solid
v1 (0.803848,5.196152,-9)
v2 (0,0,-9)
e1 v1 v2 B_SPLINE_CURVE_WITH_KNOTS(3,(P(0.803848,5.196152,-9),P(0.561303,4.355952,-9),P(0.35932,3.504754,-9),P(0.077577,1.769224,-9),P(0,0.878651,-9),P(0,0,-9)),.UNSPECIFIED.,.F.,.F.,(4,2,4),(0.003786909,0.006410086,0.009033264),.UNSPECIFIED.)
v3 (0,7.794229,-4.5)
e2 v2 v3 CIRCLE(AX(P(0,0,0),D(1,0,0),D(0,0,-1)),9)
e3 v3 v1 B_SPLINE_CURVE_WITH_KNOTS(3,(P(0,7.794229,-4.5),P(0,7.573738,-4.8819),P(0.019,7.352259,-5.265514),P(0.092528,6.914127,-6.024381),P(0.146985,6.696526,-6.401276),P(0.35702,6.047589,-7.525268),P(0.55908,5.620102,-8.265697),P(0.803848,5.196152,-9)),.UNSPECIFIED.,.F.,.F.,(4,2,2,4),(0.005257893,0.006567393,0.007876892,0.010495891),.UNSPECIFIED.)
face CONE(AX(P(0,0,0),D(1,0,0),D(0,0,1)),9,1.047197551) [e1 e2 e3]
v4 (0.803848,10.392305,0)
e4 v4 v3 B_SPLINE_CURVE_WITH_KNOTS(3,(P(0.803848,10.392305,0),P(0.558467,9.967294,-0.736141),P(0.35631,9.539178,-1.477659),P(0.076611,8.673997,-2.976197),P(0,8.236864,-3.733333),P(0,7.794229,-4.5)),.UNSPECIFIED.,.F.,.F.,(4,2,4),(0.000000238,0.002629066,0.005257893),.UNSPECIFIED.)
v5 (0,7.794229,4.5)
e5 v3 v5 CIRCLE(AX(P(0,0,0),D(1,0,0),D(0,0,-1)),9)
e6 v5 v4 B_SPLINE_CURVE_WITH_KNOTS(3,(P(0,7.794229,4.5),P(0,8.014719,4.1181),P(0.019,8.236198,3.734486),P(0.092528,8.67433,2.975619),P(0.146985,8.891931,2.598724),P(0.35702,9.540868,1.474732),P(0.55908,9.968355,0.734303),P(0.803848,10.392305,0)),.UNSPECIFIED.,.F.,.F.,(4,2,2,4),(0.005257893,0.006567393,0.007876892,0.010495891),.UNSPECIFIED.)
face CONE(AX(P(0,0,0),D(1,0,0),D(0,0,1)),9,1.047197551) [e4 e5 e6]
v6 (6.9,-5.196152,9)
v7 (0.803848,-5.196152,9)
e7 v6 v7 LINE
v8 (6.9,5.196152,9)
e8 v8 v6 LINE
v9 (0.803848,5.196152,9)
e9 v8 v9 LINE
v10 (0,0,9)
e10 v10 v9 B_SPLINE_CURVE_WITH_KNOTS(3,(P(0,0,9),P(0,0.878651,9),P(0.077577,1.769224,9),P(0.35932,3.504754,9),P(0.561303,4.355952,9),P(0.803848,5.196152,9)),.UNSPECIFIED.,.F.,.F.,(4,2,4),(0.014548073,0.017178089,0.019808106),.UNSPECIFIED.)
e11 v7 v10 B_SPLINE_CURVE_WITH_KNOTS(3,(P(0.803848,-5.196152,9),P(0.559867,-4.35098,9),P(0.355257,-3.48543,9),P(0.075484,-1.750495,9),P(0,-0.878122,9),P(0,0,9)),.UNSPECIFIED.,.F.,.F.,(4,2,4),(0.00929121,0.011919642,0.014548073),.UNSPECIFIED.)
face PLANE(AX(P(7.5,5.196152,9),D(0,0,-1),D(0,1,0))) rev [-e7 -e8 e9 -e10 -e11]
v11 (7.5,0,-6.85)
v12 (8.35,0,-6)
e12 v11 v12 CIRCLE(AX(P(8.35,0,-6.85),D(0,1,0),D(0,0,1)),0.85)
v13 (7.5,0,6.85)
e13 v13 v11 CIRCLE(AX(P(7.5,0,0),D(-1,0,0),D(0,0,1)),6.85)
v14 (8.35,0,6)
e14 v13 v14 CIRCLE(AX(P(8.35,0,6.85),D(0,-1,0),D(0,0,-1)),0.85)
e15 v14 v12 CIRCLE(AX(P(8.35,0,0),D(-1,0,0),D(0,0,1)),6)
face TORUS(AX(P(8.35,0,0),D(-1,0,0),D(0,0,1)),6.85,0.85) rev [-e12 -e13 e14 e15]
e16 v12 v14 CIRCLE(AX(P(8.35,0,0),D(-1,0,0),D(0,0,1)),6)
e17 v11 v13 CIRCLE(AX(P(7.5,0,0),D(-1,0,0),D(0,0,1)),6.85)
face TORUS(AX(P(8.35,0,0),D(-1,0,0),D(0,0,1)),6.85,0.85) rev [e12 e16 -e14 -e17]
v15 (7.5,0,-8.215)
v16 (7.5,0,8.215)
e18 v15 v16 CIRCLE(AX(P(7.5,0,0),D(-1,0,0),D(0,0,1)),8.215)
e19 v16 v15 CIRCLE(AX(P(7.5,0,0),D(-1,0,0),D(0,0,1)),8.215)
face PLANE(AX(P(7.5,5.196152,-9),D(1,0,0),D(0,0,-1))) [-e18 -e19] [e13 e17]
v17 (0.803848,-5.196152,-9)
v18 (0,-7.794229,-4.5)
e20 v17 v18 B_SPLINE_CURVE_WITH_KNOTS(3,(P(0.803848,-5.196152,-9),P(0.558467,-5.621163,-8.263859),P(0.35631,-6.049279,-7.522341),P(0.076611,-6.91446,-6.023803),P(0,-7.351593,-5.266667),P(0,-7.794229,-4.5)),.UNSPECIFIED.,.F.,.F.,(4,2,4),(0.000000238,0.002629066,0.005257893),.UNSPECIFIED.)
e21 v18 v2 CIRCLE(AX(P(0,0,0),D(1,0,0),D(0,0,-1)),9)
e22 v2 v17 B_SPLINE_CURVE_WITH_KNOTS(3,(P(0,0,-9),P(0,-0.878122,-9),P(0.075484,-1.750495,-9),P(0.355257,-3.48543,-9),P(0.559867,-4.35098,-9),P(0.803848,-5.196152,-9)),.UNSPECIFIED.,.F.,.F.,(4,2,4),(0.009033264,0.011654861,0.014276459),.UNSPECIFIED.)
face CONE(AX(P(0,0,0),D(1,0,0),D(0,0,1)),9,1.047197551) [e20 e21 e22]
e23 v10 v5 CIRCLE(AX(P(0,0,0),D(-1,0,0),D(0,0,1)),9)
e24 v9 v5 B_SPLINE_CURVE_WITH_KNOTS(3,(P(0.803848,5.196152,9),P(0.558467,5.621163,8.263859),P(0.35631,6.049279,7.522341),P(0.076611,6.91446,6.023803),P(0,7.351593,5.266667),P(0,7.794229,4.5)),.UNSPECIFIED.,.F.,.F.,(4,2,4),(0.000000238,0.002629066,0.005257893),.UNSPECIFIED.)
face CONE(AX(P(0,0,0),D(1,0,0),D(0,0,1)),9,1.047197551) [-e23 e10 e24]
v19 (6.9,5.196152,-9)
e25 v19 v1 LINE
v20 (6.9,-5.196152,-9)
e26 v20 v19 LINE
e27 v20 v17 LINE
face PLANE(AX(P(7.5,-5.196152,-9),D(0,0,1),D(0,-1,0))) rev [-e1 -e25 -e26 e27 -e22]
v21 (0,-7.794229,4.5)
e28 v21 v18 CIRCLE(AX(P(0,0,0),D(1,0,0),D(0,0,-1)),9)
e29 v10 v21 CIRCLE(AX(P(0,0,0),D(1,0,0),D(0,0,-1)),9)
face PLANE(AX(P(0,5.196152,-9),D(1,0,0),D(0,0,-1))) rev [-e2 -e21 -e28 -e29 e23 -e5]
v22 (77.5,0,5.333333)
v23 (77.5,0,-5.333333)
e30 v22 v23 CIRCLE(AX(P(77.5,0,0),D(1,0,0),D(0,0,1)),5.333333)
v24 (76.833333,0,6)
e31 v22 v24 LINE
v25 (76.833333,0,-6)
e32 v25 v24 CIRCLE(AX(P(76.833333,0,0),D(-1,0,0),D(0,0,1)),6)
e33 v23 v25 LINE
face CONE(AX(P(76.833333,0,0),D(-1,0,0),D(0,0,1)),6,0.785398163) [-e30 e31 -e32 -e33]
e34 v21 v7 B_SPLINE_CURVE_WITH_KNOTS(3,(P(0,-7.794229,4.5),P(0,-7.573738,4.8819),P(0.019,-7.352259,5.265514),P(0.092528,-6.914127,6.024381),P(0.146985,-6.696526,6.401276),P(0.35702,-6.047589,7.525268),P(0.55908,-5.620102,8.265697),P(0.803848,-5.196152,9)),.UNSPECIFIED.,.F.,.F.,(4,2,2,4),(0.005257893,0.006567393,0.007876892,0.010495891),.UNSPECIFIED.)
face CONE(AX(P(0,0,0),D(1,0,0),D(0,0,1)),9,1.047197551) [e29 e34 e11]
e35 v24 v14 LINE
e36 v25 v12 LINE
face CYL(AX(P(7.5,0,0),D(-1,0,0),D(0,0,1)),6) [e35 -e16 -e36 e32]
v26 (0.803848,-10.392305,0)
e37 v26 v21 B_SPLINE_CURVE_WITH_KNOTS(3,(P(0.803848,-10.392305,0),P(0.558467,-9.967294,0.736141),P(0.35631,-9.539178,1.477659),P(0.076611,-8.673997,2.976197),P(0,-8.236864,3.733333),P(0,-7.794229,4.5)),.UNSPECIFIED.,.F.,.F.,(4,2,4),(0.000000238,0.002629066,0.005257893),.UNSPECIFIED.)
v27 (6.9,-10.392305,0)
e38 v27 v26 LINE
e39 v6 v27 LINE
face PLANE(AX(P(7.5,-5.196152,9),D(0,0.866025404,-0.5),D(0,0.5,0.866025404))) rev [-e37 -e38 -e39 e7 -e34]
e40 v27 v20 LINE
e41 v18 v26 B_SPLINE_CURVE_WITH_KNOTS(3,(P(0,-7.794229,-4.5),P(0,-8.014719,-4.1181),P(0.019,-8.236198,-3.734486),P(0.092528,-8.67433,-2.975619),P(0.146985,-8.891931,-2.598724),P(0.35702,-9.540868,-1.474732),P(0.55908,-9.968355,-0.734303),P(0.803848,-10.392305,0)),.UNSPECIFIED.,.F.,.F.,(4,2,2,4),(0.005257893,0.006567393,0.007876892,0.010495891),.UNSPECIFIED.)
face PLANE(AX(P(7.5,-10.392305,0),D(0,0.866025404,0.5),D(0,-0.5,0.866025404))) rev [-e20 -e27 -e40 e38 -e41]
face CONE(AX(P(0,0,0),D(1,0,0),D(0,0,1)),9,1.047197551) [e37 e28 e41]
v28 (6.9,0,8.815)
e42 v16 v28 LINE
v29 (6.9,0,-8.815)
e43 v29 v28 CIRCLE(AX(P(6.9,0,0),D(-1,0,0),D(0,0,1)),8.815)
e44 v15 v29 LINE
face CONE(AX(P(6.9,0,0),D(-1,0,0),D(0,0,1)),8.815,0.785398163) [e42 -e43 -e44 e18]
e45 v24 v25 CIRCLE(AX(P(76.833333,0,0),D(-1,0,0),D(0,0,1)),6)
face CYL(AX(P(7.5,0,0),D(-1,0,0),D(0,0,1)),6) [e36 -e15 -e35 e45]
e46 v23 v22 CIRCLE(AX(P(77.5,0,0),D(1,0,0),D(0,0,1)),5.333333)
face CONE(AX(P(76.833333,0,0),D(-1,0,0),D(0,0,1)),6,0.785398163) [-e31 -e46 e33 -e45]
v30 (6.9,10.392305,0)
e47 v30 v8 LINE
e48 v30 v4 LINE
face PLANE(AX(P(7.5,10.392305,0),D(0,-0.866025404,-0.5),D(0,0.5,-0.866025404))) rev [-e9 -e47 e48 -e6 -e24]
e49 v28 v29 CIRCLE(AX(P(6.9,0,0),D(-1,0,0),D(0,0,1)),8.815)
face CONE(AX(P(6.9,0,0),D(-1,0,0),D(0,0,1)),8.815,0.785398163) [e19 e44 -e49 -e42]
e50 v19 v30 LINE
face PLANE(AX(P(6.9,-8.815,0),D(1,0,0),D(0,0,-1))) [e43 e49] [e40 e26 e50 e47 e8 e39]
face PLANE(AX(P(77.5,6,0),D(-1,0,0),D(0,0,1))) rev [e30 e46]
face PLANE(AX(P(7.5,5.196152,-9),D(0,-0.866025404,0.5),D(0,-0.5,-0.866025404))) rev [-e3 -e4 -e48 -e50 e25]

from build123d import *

# Parameters (mm, degrees)
BOSS_EXTRUDE1_DEPTH = 7.5
SKETCH4_R           = 20.03
SKETCH4_R_2         = 9
CUT_EXTRUDE1_DEPTH  = 0.9375
CUT_EXTRUDE1_DRAFT  = -60
CHAMFER2_SIZE       = 0.666666667


with BuildPart() as part:
    # Sketch3 → Boss-Extrude1 (new body)
    with BuildSketch(Plane(origin=(0, 0, 0), x_dir=(0, 0, -1), z_dir=(1, 0, 0))):
        Polygon((9, 5.196152423), (0, 10.392304845), (-9, 5.196152423), (-9, -5.196152423), (0, -10.392304845), (9, -5.196152423), align=None)
    extrude(amount=BOSS_EXTRUDE1_DEPTH)


with BuildPart() as cut_extrude1_tool:
    # Sketch4 → Cut-Extrude1 (with draft: the straight prism first)
    with BuildSketch(Plane.ZY):
        Circle(SKETCH4_R)
        Circle(SKETCH4_R_2, mode=Mode.SUBTRACT)
    extrude(amount=-CUT_EXTRUDE1_DEPTH)
    # Cut-Extrude1: the draft: its side faces are tilted about the plane it starts from
    cut_extrude1_sides = [cut_extrude1_tool.faces().sort_by_distance(p)[0] for p in [
        (0.46875, 0, -20.03),
        (0.46875, 0, -9),
    ]]
    draft(cut_extrude1_sides, Plane.ZY, CUT_EXTRUDE1_DRAFT)


with BuildPart() as part_1:
    add(part.part)

    # Cut-Extrude1: cut by cut_extrude1_tool
    add(cut_extrude1_tool.part, mode=Mode.SUBTRACT)

    # Sketch5 → Revolve1 (revolve)
    with BuildSketch(Plane.XY, mode=Mode.PRIVATE) as revolve1_sk:
        with BuildLine():
            Line((8.35, 6), (77.5, 6))
            Line((77.5, 6), (77.5, 0))
            Line((77.5, 0), (7.5, 0))
            Line((7.5, 0), (7.5, 6.85))
            ThreePointArc((7.5, 6.85), (7.748959236, 6.248959236), (8.35, 6))
        make_face()
    revolve(revolve1_sk.sketch.rotate(Axis((7.5, 0, 0), (1, 0, 0)), 90), axis=Axis((7.5, 0, 0), (1, 0, 0)))

    # Chamfer2
    chamfer2_edges = [part_1.edges().sort_by_distance(p)[0] for p in [
        (77.5, 0, -6),
    ]]
    chamfer(chamfer2_edges, length=CHAMFER2_SIZE)

    # Sketch7 → Cut-Revolve1 (revolve, cut)
    with BuildSketch(Plane.XY, mode=Mode.PRIVATE) as cut_revolve1_sk:
        Polygon((7.5, 8.215), (6.9, 8.815), (6.9, 20.03), (7.5, 20.03), align=None)
    revolve(cut_revolve1_sk.sketch.rotate(Axis((0, 0, 0), (1, 0, 0)), 90), axis=Axis((0, 0, 0), (1, 0, 0)), mode=Mode.SUBTRACT)


solid = part_1.part
